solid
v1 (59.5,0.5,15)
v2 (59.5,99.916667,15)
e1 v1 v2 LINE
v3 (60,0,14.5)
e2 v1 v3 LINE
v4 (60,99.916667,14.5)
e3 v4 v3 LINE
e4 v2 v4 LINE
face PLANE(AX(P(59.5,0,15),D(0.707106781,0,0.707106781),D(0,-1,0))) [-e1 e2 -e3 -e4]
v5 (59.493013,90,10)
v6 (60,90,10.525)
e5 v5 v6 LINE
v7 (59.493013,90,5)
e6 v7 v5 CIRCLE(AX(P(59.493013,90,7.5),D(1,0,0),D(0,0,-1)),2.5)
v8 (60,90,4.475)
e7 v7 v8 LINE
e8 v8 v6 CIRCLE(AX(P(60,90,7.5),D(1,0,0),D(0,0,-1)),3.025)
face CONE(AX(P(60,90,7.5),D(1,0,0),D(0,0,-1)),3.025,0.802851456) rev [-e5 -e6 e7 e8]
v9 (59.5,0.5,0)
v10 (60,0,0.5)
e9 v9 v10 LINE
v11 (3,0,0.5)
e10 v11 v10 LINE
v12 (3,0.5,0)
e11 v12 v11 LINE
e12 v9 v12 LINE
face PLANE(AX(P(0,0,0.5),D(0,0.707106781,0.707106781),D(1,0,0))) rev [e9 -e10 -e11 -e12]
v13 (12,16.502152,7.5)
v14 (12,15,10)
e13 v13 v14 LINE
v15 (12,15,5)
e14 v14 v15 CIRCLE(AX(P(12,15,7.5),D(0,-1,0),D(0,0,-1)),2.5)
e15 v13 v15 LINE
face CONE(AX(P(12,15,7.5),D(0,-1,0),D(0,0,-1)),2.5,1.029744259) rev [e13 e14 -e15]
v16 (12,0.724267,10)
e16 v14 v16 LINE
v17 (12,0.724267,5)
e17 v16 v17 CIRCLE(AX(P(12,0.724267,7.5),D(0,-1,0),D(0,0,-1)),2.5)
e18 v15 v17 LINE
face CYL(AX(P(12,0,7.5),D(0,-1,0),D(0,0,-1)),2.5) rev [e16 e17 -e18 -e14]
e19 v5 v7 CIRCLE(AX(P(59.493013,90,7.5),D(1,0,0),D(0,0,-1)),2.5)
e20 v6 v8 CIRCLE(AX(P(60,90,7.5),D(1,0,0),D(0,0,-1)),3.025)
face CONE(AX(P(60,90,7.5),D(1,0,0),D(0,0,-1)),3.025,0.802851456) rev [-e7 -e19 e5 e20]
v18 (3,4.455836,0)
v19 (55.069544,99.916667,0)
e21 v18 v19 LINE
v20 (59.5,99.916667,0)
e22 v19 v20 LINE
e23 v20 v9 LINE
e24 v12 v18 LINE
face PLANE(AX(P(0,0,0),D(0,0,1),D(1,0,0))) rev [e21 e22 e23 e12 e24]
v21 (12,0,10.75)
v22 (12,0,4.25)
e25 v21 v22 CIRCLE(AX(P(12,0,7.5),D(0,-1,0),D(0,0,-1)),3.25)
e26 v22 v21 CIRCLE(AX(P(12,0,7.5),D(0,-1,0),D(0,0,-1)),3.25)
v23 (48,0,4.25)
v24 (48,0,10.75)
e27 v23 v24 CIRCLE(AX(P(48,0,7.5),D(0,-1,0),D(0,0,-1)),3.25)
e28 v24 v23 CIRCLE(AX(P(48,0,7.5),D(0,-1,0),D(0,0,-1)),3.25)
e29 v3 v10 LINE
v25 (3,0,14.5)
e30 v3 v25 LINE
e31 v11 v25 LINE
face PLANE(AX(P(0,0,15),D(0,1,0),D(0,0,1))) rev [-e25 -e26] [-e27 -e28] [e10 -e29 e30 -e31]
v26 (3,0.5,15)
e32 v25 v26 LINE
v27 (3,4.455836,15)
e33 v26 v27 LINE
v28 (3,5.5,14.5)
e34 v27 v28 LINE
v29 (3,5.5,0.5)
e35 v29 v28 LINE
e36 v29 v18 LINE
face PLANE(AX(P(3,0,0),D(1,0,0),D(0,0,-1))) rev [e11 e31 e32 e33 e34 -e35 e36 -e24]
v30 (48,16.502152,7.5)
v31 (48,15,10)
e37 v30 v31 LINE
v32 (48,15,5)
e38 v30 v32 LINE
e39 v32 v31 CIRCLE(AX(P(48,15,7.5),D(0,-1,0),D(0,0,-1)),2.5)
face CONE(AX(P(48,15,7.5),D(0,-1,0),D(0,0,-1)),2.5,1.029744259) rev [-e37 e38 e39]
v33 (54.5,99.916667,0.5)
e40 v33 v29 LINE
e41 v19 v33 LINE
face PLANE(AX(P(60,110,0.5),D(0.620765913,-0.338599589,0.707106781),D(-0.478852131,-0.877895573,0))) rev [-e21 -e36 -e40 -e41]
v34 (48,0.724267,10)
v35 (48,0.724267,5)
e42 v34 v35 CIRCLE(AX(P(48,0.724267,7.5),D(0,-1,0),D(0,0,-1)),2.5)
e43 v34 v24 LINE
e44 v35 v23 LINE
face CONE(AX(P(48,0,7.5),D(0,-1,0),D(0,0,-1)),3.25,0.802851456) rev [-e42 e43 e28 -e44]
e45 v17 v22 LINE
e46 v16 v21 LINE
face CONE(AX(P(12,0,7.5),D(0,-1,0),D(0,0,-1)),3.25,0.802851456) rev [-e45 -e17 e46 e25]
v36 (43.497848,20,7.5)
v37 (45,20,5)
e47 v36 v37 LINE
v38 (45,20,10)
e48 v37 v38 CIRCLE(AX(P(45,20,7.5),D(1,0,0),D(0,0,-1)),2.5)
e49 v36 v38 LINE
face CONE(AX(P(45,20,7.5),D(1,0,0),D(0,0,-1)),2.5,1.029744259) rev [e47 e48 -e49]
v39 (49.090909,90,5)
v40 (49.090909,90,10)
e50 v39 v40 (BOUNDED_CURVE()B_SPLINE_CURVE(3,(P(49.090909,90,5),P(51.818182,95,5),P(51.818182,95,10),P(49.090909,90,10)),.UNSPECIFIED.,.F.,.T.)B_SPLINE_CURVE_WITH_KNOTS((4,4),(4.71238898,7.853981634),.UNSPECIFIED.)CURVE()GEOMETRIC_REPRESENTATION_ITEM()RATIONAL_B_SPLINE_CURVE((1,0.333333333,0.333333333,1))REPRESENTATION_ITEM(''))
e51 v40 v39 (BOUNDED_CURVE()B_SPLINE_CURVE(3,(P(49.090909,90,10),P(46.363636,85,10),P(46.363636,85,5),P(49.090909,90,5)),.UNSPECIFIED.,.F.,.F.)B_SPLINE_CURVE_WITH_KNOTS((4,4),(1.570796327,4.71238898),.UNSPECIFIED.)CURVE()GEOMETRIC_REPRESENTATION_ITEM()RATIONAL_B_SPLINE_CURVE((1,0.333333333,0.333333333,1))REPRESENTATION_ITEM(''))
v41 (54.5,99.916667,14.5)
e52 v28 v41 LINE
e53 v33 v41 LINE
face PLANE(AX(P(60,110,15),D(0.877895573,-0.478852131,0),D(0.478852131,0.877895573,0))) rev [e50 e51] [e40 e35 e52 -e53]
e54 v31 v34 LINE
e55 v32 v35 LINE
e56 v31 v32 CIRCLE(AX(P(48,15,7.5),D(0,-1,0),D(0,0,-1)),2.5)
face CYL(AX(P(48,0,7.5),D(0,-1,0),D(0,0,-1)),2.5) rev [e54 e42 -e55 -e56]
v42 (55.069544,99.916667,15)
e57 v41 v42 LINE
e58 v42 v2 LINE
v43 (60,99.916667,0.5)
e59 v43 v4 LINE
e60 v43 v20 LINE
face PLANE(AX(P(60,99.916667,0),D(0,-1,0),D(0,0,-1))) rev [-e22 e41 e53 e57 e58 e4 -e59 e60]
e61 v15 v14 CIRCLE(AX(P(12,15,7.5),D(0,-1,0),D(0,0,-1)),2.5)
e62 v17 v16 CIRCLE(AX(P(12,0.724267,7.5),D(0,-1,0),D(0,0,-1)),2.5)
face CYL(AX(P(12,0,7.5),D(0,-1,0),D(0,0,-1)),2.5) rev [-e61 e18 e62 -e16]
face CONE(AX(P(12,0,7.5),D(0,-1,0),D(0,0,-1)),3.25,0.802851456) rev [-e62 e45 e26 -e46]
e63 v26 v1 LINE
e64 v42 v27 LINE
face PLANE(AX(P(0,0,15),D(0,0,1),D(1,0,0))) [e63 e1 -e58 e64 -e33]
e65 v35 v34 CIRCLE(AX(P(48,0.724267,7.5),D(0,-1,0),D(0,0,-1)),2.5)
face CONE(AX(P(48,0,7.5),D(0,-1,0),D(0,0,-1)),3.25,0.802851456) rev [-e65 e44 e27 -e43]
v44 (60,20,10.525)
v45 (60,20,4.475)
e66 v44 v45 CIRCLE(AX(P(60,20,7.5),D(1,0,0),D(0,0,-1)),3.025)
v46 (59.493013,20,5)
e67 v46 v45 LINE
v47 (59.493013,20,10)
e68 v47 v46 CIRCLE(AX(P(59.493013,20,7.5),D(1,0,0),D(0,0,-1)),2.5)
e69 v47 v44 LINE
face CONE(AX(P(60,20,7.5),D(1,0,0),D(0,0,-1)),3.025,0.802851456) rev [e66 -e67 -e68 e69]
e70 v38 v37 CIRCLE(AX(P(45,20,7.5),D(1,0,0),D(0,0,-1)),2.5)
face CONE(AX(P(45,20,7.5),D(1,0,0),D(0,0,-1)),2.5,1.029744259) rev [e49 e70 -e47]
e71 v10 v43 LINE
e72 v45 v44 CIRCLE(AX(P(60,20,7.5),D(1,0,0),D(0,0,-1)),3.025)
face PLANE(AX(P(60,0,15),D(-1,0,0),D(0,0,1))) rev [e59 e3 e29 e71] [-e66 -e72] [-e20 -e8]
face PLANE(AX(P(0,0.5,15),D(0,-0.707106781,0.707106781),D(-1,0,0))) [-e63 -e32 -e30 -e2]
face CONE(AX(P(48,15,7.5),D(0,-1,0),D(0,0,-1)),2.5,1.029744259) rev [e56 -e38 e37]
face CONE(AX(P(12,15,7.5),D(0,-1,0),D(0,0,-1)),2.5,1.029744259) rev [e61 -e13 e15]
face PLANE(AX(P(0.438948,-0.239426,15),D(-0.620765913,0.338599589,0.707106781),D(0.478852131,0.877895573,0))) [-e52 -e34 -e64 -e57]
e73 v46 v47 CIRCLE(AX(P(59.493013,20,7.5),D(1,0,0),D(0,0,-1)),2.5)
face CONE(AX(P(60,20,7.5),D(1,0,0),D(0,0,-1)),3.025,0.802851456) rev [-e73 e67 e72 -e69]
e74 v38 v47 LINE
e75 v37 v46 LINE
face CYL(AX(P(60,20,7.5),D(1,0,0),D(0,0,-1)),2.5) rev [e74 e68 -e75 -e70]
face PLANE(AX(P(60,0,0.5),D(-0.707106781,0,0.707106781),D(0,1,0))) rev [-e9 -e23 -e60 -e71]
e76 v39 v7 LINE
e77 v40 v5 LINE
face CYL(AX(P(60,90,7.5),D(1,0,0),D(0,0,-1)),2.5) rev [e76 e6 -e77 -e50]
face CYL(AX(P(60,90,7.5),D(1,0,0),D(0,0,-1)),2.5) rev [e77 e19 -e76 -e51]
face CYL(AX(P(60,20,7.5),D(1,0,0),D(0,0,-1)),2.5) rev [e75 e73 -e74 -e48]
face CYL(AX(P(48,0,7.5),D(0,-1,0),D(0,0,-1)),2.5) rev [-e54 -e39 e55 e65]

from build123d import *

# Parameters (mm, degrees)
EXTRUDE_1_DEPTH              = 15
HOLE_WIZARD_M6_1_D           = 5
HOLE_WIZARD_M6_1_DEPTH       = 15
HOLE_WIZARD_M6_1_CSINK_D     = 6.5
HOLE_WIZARD_M6_1_CSINK_ANGLE = 92
HOLE_WIZARD_M6_1_TIP         = 1.502151548
HOLE_WIZARD_M6_2_D           = 5
HOLE_WIZARD_M6_2_DEPTH       = 15
HOLE_WIZARD_M6_2_CSINK_D     = 6.05
HOLE_WIZARD_M6_2_CSINK_ANGLE = 92
HOLE_WIZARD_M6_2_TIP         = 1.502151548
CHAMFER_1_SIZE               = 0.5
SKETCH_7_W                   = 5.5
SKETCH_7_H                   = 10.083333333
SKETCH_7_W_2                 = 3
SKETCH_7_H_2                 = 20
CUT_EXTRUDE_1_DEPTH          = 127.194294641


with BuildPart() as part:
    # 草图1 → 凸台-拉伸1 (new body)
    with BuildSketch(Plane.XY):
        Polygon((0, 0), (60, 0), (60, 110), align=None)
    extrude(amount=EXTRUDE_1_DEPTH)

    # M6 螺纹孔1
    with Locations(Plane(origin=(0, 0, 0), x_dir=(-1, 0, 0), z_dir=(0, -1, 0))):
        with Locations((-48, -7.5), (-12, -7.5)):
            CounterSinkHole(HOLE_WIZARD_M6_1_D / 2, HOLE_WIZARD_M6_1_CSINK_D / 2, depth=HOLE_WIZARD_M6_1_DEPTH, counter_sink_angle=HOLE_WIZARD_M6_1_CSINK_ANGLE)
            with Locations((0, 0, -(HOLE_WIZARD_M6_1_DEPTH + HOLE_WIZARD_M6_1_TIP / 2))):  # 118° drill point
                Cone(0, HOLE_WIZARD_M6_1_D / 2, HOLE_WIZARD_M6_1_TIP, mode=Mode.SUBTRACT)

    # M6 螺纹孔2
    with Locations(Plane(origin=(60, 0, 0), x_dir=(0, 0, -1), z_dir=(1, 0, 0))):
        with Locations((-7.5, 20), (-7.5, 90)):
            CounterSinkHole(HOLE_WIZARD_M6_2_D / 2, HOLE_WIZARD_M6_2_CSINK_D / 2, depth=HOLE_WIZARD_M6_2_DEPTH, counter_sink_angle=HOLE_WIZARD_M6_2_CSINK_ANGLE)
            with Locations((0, 0, -(HOLE_WIZARD_M6_2_DEPTH + HOLE_WIZARD_M6_2_TIP / 2))):  # 118° drill point
                Cone(0, HOLE_WIZARD_M6_2_D / 2, HOLE_WIZARD_M6_2_TIP, mode=Mode.SUBTRACT)

    # 倒角1
    chamfer_1_edges = [part.edges().sort_by_distance(p)[0] for p in [
        (60, 55, 15),
        (60, 55, 0),
        (30, 55, 15),
        (30, 0, 0),
        (30, 55, 0),
        (30, 0, 15),
    ]]
    chamfer(chamfer_1_edges, length=CHAMFER_1_SIZE)

    # 草图7 → 切除-拉伸1 (cut, through all)
    with BuildSketch(Plane.XY.offset(15)):
        with Locations((57.25, 104.958333334)):
            Rectangle(SKETCH_7_W, SKETCH_7_H)
        with Locations((1.5, 10)):
            Rectangle(SKETCH_7_W_2, SKETCH_7_H_2)
    extrude(amount=-CUT_EXTRUDE_1_DEPTH, mode=Mode.SUBTRACT)


solid = part.part
